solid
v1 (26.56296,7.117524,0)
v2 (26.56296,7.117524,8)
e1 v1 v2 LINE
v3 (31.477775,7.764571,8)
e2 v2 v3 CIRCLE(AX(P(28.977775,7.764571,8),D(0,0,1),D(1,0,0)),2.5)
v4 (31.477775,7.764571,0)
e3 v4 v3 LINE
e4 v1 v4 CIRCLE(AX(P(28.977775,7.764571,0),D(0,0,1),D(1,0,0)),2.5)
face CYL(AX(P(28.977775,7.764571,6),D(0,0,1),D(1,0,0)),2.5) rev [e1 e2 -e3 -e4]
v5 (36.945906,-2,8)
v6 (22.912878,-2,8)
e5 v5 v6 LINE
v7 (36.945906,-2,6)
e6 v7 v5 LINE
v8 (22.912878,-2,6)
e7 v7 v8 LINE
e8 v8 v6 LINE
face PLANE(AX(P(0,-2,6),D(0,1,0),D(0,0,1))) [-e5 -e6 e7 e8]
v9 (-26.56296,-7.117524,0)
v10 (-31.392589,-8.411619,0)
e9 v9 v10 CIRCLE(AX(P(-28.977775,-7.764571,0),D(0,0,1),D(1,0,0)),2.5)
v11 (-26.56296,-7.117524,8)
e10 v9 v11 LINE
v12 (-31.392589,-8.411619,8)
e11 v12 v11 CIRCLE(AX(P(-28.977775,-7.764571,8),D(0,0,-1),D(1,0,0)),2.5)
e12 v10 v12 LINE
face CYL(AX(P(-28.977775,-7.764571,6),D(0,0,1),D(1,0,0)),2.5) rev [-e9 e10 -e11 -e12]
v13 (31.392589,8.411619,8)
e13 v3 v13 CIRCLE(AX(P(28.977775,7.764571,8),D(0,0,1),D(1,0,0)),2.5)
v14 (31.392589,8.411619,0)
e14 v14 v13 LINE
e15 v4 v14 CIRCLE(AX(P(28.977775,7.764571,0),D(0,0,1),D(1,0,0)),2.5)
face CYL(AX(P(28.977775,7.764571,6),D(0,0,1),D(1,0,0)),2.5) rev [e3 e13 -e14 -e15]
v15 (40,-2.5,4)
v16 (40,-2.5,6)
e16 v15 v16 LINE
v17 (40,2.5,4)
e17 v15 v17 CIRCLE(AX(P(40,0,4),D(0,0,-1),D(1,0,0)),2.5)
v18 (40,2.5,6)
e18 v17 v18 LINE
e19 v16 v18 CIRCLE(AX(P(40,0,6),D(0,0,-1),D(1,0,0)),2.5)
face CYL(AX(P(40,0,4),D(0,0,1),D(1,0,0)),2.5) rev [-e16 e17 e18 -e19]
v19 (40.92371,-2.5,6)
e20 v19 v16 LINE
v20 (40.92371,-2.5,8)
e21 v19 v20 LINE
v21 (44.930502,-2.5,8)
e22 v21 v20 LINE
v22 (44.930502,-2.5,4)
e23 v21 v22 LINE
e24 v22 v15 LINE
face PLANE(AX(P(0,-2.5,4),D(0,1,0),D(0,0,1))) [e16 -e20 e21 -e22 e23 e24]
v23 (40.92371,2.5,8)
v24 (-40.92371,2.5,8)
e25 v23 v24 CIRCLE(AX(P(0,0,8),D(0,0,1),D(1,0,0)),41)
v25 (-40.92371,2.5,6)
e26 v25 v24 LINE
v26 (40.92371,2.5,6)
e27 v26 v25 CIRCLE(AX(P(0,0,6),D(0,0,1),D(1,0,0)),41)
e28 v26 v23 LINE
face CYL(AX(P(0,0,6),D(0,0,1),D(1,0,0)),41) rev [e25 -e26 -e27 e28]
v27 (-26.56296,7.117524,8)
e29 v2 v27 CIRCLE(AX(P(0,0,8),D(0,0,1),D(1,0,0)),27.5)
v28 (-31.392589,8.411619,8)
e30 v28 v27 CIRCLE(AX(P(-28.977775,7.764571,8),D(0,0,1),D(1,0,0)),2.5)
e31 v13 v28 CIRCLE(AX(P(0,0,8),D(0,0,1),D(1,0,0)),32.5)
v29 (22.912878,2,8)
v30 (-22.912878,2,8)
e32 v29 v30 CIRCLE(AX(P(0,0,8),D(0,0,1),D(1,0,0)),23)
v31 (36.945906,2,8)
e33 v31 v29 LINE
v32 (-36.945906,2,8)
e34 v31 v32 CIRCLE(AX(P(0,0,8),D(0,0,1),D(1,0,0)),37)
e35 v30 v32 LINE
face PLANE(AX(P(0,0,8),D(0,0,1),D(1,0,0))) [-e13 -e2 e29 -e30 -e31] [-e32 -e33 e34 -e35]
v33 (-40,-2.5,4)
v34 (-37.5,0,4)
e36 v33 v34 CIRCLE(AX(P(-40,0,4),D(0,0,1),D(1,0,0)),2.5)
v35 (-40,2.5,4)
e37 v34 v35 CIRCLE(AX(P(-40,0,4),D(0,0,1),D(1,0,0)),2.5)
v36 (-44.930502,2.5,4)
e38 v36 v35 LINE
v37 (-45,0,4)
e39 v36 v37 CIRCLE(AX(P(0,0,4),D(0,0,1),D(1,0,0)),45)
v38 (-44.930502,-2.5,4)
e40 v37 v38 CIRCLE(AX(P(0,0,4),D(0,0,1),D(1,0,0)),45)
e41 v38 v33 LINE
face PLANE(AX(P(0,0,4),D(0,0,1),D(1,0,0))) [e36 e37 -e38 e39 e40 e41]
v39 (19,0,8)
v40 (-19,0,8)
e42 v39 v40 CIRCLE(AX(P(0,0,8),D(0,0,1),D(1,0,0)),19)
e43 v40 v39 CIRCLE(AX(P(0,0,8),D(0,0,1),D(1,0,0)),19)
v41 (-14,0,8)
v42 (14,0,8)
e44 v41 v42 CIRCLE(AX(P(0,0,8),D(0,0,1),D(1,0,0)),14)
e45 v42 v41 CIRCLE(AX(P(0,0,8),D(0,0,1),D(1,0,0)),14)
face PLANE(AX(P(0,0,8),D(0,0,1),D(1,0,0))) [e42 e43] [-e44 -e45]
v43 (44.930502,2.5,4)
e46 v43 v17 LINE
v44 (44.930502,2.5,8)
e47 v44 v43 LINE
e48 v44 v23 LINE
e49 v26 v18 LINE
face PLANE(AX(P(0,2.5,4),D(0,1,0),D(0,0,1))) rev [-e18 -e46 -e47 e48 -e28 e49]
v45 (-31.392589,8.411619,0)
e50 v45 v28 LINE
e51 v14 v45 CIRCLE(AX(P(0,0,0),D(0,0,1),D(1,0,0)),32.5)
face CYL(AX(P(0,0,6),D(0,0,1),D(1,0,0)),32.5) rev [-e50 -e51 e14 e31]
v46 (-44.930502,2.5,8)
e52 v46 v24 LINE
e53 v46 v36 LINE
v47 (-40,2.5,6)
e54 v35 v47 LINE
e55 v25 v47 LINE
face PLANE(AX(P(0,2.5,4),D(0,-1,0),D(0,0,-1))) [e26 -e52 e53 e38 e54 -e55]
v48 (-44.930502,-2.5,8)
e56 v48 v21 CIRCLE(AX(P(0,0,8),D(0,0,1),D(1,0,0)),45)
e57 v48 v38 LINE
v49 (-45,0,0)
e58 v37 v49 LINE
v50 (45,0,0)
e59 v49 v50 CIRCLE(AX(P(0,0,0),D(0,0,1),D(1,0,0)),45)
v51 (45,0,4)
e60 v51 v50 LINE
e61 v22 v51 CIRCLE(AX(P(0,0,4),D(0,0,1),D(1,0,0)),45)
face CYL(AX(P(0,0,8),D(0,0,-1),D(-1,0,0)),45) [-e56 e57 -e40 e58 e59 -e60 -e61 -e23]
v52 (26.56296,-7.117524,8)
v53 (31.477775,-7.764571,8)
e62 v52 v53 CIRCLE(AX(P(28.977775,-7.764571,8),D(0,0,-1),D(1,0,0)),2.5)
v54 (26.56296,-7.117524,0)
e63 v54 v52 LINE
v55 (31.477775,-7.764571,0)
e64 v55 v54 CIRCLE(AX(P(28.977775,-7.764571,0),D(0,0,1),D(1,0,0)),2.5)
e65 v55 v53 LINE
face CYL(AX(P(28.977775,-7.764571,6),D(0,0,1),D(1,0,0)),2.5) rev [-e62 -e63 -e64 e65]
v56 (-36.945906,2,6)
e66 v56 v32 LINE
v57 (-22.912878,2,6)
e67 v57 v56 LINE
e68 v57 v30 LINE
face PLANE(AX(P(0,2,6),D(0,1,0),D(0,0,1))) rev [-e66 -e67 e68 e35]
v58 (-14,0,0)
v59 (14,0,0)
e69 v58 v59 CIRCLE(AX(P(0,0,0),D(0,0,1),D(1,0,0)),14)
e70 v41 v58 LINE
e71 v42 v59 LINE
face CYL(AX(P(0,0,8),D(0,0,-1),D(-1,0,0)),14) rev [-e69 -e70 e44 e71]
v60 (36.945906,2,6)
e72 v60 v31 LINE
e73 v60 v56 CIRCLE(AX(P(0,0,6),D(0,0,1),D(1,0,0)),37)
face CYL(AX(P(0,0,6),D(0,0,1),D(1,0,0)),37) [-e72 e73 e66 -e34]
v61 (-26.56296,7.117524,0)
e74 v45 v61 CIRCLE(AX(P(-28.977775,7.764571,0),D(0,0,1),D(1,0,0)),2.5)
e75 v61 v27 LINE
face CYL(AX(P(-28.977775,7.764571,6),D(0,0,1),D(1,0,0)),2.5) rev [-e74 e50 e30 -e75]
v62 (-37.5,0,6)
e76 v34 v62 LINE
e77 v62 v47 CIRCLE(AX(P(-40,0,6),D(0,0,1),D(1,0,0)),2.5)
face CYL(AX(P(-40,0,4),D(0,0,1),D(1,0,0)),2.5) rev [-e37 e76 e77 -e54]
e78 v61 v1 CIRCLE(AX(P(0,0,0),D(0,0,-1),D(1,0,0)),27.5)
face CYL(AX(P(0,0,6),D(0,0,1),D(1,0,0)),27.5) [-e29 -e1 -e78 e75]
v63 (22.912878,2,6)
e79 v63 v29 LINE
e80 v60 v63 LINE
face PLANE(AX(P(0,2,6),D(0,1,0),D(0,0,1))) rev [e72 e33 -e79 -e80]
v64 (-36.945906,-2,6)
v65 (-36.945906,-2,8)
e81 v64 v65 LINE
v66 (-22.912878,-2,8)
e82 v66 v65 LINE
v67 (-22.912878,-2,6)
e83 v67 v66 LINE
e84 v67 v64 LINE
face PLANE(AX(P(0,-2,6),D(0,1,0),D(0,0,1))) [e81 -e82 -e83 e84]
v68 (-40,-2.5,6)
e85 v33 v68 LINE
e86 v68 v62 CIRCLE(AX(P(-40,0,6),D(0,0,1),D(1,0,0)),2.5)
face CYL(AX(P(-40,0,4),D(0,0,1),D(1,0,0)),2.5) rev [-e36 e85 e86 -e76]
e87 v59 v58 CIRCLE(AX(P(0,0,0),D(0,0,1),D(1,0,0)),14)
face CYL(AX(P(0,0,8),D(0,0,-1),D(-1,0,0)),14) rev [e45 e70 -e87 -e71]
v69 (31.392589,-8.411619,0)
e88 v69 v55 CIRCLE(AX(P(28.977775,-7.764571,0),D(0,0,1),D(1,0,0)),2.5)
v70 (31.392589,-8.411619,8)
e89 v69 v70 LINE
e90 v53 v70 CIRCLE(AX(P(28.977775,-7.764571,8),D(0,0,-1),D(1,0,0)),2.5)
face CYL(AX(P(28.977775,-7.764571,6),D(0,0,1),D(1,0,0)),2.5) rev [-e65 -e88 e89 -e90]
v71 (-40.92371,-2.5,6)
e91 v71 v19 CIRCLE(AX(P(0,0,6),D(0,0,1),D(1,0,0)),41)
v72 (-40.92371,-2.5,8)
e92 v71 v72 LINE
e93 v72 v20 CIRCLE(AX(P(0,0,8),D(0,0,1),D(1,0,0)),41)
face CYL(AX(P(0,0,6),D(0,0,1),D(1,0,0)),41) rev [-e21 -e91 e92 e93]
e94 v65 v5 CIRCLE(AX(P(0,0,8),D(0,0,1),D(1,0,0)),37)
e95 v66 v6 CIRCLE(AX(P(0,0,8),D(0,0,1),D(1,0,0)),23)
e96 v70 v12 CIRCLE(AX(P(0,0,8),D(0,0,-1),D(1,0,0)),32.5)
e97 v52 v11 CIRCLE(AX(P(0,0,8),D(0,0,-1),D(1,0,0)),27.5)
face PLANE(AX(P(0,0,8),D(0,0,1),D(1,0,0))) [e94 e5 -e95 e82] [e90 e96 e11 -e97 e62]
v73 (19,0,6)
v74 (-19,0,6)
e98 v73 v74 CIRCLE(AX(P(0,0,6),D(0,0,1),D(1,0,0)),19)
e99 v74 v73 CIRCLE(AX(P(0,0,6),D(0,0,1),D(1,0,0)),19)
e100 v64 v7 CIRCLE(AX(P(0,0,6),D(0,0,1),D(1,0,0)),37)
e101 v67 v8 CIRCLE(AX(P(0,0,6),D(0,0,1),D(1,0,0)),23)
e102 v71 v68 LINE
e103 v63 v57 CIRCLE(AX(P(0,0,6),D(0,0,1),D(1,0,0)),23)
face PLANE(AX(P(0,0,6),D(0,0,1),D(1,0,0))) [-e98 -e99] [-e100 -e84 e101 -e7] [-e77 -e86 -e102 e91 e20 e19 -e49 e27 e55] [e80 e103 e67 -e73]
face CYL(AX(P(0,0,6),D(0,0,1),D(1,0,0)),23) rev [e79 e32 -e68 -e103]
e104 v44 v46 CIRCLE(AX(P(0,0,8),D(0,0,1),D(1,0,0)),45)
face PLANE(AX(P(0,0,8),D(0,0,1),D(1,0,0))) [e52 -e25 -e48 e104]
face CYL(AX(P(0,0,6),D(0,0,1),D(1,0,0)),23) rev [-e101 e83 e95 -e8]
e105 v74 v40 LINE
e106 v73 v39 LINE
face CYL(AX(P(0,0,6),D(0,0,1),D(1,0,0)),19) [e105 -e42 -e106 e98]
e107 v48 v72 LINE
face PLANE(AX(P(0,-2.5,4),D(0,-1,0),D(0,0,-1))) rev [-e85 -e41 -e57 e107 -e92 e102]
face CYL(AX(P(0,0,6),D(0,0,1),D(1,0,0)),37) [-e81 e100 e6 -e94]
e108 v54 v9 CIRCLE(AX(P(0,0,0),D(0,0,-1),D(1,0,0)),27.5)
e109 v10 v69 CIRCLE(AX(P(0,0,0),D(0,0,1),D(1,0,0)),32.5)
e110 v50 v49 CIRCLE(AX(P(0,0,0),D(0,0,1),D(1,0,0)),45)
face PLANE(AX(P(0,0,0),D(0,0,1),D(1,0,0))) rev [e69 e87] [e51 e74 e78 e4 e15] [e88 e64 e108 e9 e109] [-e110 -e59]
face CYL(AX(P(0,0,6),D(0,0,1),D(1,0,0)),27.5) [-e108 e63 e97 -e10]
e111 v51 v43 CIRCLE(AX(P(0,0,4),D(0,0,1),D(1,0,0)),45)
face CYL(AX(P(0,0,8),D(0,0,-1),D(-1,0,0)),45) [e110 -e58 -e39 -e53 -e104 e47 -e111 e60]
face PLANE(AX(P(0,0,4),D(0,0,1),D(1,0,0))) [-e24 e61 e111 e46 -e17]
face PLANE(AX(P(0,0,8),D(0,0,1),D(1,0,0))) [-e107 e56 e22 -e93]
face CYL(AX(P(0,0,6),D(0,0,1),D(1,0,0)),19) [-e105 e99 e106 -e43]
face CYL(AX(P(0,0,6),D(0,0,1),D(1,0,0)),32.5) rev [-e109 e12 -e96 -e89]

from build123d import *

# Parameters (mm, degrees)
SKETCH1_R           = 45
SKETCH1_R_2         = 14
BOSS_EXTRUDE1_DEPTH = 8
SKETCH2_R           = 41
SKETCH2_R_2         = 37
SKETCH2_R_3         = 23
SKETCH2_R_4         = 19
CUT_EXTRUDE1_DEPTH  = 2
CUT_EXTRUDE2_DEPTH  = 100
CUT_EXTRUDE3_DEPTH  = 4
CUT_EXTRUDE4_DEPTH  = 2


with BuildPart() as part:
    # Sketch1 → Boss-Extrude1 (new body)
    with BuildSketch(Plane.XY):
        Circle(SKETCH1_R)
        Circle(SKETCH1_R_2, mode=Mode.SUBTRACT)
    extrude(amount=BOSS_EXTRUDE1_DEPTH)

    # Sketch2 → Cut-Extrude1 (cut)
    # profile 1 of 4: a face of its own
    with BuildSketch(Plane.XY.offset(8)):
        Circle(SKETCH2_R)
        Circle(SKETCH2_R_2, mode=Mode.SUBTRACT)
    # profile 2 of 4: a face of its own
    with BuildSketch(Plane.XY.offset(8)):
        Circle(SKETCH2_R_3)
        Circle(SKETCH2_R_4, mode=Mode.SUBTRACT)
    # profile 3 of 4: a face of its own
    with BuildSketch(Plane.XY.offset(8)):
        with BuildLine():
            ThreePointArc((31.392589354, 8.411618966), (0, 32.5), (-31.392589354, 8.411618966))
            ThreePointArc((-31.392589354, 8.411618966), (-29.624822401, 5.349756787), (-26.562960223, 7.11752374))
            ThreePointArc((-26.562960223, 7.11752374), (0, 27.5), (26.562960223, 7.11752374))
            ThreePointArc((26.562960223, 7.11752374), (29.624822401, 5.349756787), (31.392589354, 8.411618966))
        make_face()
    # profile 4 of 4: a face of its own
    with BuildSketch(Plane.XY.offset(8)):
        with BuildLine():
            ThreePointArc((-31.392589354, -8.411618966), (-29.624822401, -5.349756787), (-26.562960223, -7.11752374))
            ThreePointArc((-26.562960223, -7.11752374), (0, -27.5), (26.562960223, -7.11752374))
            ThreePointArc((26.562960223, -7.11752374), (29.624822401, -5.349756787), (31.392589354, -8.411618966))
            ThreePointArc((31.392589354, -8.411618966), (0, -32.5), (-31.392589354, -8.411618966))
        make_face()
    extrude(amount=-CUT_EXTRUDE1_DEPTH, mode=Mode.SUBTRACT)

    # Sketch3 → Cut-Extrude2 (cut)
    with BuildSketch(Plane.XY.offset(6)):
        with BuildLine():
            ThreePointArc((31.392589354, 8.411618966), (0, 32.5), (-31.392589354, 8.411618966))
            ThreePointArc((-31.392589354, 8.411618966), (-29.624822401, 5.349756787), (-26.562960223, 7.11752374))
            ThreePointArc((-26.562960223, 7.11752374), (0, 27.5), (26.562960223, 7.11752374))
            ThreePointArc((26.562960223, 7.11752374), (29.624822401, 5.349756787), (31.392589354, 8.411618966))
        make_face()
        with BuildLine():
            ThreePointArc((-26.562960223, -7.11752374), (-29.624822401, -5.349756787), (-31.392589354, -8.411618966))
            ThreePointArc((-31.392589354, -8.411618966), (0, -32.5), (31.392589354, -8.411618966))
            ThreePointArc((31.392589354, -8.411618966), (29.624822401, -5.349756787), (26.562960223, -7.11752374))
            ThreePointArc((26.562960223, -7.11752374), (0, -27.5), (-26.562960223, -7.11752374))
        make_face()
    extrude(amount=-CUT_EXTRUDE2_DEPTH, mode=Mode.SUBTRACT)

    # Sketch4<3> → Cut-Extrude3 (cut)
    with BuildSketch(Plane.XY.offset(8)):
        with BuildLine():
            Line((-45, -2.5), (-40, -2.5))
            ThreePointArc((-40, -2.5), (-37.5, 0), (-40, 2.5))
            Line((-40, 2.5), (-45, 2.5))
            ThreePointArc((-45, 2.5), (-47.5, 0), (-45, -2.5))
        make_face()
        with BuildLine():
            ThreePointArc((40, -2.5), (37.5, 0), (40, 2.5))
            Line((40, 2.5), (45, 2.5))
            ThreePointArc((45, 2.5), (47.5, 0), (45, -2.5))
            Line((45, -2.5), (40, -2.5))
        make_face()
    extrude(amount=-CUT_EXTRUDE3_DEPTH, mode=Mode.SUBTRACT)

    # 草图4<3> → Cut-Extrude4 (cut)
    with BuildSketch(Plane.XY.offset(8)):
        with BuildLine():
            Line((22.912878475, -2), (36.945906404, -2))
            ThreePointArc((36.945906404, -2), (36.986474129, -1.000365698), (37, 0))
            ThreePointArc((37, 0), (36.986474129, 1.000365698), (36.945906404, 2))
            Line((36.945906404, 2), (22.912878475, 2))
            ThreePointArc((22.912878475, 2), (22.978209296, 1.00094832), (23, 0))
            ThreePointArc((23, 0), (22.978209296, -1.00094832), (22.912878475, -2))
        make_face()
        with BuildLine():
            ThreePointArc((-36.945906404, 2), (-37, 0), (-36.945906404, -2))
            Line((-36.945906404, -2), (-22.912878475, -2))
            ThreePointArc((-22.912878475, -2), (-23, 0), (-22.912878475, 2))
            Line((-22.912878475, 2), (-36.945906404, 2))
        make_face()
        with BuildLine():
            Line((22.912878475, -2), (36.945906404, -2))
            ThreePointArc((36.945906404, -2), (36.986474129, -1.000365698), (37, 0))
            ThreePointArc((37, 0), (36.986474129, 1.000365698), (36.945906404, 2))
            Line((36.945906404, 2), (22.912878475, 2))
            ThreePointArc((22.912878475, 2), (22.978209296, 1.00094832), (23, 0))
            ThreePointArc((23, 0), (22.978209296, -1.00094832), (22.912878475, -2))
        make_face()
        with BuildLine():
            ThreePointArc((-36.945906404, 2), (-37, 0), (-36.945906404, -2))
            Line((-36.945906404, -2), (-22.912878475, -2))
            ThreePointArc((-22.912878475, -2), (-23, 0), (-22.912878475, 2))
            Line((-22.912878475, 2), (-36.945906404, 2))
        make_face()
    extrude(amount=-CUT_EXTRUDE4_DEPTH, mode=Mode.SUBTRACT)


solid = part.part
